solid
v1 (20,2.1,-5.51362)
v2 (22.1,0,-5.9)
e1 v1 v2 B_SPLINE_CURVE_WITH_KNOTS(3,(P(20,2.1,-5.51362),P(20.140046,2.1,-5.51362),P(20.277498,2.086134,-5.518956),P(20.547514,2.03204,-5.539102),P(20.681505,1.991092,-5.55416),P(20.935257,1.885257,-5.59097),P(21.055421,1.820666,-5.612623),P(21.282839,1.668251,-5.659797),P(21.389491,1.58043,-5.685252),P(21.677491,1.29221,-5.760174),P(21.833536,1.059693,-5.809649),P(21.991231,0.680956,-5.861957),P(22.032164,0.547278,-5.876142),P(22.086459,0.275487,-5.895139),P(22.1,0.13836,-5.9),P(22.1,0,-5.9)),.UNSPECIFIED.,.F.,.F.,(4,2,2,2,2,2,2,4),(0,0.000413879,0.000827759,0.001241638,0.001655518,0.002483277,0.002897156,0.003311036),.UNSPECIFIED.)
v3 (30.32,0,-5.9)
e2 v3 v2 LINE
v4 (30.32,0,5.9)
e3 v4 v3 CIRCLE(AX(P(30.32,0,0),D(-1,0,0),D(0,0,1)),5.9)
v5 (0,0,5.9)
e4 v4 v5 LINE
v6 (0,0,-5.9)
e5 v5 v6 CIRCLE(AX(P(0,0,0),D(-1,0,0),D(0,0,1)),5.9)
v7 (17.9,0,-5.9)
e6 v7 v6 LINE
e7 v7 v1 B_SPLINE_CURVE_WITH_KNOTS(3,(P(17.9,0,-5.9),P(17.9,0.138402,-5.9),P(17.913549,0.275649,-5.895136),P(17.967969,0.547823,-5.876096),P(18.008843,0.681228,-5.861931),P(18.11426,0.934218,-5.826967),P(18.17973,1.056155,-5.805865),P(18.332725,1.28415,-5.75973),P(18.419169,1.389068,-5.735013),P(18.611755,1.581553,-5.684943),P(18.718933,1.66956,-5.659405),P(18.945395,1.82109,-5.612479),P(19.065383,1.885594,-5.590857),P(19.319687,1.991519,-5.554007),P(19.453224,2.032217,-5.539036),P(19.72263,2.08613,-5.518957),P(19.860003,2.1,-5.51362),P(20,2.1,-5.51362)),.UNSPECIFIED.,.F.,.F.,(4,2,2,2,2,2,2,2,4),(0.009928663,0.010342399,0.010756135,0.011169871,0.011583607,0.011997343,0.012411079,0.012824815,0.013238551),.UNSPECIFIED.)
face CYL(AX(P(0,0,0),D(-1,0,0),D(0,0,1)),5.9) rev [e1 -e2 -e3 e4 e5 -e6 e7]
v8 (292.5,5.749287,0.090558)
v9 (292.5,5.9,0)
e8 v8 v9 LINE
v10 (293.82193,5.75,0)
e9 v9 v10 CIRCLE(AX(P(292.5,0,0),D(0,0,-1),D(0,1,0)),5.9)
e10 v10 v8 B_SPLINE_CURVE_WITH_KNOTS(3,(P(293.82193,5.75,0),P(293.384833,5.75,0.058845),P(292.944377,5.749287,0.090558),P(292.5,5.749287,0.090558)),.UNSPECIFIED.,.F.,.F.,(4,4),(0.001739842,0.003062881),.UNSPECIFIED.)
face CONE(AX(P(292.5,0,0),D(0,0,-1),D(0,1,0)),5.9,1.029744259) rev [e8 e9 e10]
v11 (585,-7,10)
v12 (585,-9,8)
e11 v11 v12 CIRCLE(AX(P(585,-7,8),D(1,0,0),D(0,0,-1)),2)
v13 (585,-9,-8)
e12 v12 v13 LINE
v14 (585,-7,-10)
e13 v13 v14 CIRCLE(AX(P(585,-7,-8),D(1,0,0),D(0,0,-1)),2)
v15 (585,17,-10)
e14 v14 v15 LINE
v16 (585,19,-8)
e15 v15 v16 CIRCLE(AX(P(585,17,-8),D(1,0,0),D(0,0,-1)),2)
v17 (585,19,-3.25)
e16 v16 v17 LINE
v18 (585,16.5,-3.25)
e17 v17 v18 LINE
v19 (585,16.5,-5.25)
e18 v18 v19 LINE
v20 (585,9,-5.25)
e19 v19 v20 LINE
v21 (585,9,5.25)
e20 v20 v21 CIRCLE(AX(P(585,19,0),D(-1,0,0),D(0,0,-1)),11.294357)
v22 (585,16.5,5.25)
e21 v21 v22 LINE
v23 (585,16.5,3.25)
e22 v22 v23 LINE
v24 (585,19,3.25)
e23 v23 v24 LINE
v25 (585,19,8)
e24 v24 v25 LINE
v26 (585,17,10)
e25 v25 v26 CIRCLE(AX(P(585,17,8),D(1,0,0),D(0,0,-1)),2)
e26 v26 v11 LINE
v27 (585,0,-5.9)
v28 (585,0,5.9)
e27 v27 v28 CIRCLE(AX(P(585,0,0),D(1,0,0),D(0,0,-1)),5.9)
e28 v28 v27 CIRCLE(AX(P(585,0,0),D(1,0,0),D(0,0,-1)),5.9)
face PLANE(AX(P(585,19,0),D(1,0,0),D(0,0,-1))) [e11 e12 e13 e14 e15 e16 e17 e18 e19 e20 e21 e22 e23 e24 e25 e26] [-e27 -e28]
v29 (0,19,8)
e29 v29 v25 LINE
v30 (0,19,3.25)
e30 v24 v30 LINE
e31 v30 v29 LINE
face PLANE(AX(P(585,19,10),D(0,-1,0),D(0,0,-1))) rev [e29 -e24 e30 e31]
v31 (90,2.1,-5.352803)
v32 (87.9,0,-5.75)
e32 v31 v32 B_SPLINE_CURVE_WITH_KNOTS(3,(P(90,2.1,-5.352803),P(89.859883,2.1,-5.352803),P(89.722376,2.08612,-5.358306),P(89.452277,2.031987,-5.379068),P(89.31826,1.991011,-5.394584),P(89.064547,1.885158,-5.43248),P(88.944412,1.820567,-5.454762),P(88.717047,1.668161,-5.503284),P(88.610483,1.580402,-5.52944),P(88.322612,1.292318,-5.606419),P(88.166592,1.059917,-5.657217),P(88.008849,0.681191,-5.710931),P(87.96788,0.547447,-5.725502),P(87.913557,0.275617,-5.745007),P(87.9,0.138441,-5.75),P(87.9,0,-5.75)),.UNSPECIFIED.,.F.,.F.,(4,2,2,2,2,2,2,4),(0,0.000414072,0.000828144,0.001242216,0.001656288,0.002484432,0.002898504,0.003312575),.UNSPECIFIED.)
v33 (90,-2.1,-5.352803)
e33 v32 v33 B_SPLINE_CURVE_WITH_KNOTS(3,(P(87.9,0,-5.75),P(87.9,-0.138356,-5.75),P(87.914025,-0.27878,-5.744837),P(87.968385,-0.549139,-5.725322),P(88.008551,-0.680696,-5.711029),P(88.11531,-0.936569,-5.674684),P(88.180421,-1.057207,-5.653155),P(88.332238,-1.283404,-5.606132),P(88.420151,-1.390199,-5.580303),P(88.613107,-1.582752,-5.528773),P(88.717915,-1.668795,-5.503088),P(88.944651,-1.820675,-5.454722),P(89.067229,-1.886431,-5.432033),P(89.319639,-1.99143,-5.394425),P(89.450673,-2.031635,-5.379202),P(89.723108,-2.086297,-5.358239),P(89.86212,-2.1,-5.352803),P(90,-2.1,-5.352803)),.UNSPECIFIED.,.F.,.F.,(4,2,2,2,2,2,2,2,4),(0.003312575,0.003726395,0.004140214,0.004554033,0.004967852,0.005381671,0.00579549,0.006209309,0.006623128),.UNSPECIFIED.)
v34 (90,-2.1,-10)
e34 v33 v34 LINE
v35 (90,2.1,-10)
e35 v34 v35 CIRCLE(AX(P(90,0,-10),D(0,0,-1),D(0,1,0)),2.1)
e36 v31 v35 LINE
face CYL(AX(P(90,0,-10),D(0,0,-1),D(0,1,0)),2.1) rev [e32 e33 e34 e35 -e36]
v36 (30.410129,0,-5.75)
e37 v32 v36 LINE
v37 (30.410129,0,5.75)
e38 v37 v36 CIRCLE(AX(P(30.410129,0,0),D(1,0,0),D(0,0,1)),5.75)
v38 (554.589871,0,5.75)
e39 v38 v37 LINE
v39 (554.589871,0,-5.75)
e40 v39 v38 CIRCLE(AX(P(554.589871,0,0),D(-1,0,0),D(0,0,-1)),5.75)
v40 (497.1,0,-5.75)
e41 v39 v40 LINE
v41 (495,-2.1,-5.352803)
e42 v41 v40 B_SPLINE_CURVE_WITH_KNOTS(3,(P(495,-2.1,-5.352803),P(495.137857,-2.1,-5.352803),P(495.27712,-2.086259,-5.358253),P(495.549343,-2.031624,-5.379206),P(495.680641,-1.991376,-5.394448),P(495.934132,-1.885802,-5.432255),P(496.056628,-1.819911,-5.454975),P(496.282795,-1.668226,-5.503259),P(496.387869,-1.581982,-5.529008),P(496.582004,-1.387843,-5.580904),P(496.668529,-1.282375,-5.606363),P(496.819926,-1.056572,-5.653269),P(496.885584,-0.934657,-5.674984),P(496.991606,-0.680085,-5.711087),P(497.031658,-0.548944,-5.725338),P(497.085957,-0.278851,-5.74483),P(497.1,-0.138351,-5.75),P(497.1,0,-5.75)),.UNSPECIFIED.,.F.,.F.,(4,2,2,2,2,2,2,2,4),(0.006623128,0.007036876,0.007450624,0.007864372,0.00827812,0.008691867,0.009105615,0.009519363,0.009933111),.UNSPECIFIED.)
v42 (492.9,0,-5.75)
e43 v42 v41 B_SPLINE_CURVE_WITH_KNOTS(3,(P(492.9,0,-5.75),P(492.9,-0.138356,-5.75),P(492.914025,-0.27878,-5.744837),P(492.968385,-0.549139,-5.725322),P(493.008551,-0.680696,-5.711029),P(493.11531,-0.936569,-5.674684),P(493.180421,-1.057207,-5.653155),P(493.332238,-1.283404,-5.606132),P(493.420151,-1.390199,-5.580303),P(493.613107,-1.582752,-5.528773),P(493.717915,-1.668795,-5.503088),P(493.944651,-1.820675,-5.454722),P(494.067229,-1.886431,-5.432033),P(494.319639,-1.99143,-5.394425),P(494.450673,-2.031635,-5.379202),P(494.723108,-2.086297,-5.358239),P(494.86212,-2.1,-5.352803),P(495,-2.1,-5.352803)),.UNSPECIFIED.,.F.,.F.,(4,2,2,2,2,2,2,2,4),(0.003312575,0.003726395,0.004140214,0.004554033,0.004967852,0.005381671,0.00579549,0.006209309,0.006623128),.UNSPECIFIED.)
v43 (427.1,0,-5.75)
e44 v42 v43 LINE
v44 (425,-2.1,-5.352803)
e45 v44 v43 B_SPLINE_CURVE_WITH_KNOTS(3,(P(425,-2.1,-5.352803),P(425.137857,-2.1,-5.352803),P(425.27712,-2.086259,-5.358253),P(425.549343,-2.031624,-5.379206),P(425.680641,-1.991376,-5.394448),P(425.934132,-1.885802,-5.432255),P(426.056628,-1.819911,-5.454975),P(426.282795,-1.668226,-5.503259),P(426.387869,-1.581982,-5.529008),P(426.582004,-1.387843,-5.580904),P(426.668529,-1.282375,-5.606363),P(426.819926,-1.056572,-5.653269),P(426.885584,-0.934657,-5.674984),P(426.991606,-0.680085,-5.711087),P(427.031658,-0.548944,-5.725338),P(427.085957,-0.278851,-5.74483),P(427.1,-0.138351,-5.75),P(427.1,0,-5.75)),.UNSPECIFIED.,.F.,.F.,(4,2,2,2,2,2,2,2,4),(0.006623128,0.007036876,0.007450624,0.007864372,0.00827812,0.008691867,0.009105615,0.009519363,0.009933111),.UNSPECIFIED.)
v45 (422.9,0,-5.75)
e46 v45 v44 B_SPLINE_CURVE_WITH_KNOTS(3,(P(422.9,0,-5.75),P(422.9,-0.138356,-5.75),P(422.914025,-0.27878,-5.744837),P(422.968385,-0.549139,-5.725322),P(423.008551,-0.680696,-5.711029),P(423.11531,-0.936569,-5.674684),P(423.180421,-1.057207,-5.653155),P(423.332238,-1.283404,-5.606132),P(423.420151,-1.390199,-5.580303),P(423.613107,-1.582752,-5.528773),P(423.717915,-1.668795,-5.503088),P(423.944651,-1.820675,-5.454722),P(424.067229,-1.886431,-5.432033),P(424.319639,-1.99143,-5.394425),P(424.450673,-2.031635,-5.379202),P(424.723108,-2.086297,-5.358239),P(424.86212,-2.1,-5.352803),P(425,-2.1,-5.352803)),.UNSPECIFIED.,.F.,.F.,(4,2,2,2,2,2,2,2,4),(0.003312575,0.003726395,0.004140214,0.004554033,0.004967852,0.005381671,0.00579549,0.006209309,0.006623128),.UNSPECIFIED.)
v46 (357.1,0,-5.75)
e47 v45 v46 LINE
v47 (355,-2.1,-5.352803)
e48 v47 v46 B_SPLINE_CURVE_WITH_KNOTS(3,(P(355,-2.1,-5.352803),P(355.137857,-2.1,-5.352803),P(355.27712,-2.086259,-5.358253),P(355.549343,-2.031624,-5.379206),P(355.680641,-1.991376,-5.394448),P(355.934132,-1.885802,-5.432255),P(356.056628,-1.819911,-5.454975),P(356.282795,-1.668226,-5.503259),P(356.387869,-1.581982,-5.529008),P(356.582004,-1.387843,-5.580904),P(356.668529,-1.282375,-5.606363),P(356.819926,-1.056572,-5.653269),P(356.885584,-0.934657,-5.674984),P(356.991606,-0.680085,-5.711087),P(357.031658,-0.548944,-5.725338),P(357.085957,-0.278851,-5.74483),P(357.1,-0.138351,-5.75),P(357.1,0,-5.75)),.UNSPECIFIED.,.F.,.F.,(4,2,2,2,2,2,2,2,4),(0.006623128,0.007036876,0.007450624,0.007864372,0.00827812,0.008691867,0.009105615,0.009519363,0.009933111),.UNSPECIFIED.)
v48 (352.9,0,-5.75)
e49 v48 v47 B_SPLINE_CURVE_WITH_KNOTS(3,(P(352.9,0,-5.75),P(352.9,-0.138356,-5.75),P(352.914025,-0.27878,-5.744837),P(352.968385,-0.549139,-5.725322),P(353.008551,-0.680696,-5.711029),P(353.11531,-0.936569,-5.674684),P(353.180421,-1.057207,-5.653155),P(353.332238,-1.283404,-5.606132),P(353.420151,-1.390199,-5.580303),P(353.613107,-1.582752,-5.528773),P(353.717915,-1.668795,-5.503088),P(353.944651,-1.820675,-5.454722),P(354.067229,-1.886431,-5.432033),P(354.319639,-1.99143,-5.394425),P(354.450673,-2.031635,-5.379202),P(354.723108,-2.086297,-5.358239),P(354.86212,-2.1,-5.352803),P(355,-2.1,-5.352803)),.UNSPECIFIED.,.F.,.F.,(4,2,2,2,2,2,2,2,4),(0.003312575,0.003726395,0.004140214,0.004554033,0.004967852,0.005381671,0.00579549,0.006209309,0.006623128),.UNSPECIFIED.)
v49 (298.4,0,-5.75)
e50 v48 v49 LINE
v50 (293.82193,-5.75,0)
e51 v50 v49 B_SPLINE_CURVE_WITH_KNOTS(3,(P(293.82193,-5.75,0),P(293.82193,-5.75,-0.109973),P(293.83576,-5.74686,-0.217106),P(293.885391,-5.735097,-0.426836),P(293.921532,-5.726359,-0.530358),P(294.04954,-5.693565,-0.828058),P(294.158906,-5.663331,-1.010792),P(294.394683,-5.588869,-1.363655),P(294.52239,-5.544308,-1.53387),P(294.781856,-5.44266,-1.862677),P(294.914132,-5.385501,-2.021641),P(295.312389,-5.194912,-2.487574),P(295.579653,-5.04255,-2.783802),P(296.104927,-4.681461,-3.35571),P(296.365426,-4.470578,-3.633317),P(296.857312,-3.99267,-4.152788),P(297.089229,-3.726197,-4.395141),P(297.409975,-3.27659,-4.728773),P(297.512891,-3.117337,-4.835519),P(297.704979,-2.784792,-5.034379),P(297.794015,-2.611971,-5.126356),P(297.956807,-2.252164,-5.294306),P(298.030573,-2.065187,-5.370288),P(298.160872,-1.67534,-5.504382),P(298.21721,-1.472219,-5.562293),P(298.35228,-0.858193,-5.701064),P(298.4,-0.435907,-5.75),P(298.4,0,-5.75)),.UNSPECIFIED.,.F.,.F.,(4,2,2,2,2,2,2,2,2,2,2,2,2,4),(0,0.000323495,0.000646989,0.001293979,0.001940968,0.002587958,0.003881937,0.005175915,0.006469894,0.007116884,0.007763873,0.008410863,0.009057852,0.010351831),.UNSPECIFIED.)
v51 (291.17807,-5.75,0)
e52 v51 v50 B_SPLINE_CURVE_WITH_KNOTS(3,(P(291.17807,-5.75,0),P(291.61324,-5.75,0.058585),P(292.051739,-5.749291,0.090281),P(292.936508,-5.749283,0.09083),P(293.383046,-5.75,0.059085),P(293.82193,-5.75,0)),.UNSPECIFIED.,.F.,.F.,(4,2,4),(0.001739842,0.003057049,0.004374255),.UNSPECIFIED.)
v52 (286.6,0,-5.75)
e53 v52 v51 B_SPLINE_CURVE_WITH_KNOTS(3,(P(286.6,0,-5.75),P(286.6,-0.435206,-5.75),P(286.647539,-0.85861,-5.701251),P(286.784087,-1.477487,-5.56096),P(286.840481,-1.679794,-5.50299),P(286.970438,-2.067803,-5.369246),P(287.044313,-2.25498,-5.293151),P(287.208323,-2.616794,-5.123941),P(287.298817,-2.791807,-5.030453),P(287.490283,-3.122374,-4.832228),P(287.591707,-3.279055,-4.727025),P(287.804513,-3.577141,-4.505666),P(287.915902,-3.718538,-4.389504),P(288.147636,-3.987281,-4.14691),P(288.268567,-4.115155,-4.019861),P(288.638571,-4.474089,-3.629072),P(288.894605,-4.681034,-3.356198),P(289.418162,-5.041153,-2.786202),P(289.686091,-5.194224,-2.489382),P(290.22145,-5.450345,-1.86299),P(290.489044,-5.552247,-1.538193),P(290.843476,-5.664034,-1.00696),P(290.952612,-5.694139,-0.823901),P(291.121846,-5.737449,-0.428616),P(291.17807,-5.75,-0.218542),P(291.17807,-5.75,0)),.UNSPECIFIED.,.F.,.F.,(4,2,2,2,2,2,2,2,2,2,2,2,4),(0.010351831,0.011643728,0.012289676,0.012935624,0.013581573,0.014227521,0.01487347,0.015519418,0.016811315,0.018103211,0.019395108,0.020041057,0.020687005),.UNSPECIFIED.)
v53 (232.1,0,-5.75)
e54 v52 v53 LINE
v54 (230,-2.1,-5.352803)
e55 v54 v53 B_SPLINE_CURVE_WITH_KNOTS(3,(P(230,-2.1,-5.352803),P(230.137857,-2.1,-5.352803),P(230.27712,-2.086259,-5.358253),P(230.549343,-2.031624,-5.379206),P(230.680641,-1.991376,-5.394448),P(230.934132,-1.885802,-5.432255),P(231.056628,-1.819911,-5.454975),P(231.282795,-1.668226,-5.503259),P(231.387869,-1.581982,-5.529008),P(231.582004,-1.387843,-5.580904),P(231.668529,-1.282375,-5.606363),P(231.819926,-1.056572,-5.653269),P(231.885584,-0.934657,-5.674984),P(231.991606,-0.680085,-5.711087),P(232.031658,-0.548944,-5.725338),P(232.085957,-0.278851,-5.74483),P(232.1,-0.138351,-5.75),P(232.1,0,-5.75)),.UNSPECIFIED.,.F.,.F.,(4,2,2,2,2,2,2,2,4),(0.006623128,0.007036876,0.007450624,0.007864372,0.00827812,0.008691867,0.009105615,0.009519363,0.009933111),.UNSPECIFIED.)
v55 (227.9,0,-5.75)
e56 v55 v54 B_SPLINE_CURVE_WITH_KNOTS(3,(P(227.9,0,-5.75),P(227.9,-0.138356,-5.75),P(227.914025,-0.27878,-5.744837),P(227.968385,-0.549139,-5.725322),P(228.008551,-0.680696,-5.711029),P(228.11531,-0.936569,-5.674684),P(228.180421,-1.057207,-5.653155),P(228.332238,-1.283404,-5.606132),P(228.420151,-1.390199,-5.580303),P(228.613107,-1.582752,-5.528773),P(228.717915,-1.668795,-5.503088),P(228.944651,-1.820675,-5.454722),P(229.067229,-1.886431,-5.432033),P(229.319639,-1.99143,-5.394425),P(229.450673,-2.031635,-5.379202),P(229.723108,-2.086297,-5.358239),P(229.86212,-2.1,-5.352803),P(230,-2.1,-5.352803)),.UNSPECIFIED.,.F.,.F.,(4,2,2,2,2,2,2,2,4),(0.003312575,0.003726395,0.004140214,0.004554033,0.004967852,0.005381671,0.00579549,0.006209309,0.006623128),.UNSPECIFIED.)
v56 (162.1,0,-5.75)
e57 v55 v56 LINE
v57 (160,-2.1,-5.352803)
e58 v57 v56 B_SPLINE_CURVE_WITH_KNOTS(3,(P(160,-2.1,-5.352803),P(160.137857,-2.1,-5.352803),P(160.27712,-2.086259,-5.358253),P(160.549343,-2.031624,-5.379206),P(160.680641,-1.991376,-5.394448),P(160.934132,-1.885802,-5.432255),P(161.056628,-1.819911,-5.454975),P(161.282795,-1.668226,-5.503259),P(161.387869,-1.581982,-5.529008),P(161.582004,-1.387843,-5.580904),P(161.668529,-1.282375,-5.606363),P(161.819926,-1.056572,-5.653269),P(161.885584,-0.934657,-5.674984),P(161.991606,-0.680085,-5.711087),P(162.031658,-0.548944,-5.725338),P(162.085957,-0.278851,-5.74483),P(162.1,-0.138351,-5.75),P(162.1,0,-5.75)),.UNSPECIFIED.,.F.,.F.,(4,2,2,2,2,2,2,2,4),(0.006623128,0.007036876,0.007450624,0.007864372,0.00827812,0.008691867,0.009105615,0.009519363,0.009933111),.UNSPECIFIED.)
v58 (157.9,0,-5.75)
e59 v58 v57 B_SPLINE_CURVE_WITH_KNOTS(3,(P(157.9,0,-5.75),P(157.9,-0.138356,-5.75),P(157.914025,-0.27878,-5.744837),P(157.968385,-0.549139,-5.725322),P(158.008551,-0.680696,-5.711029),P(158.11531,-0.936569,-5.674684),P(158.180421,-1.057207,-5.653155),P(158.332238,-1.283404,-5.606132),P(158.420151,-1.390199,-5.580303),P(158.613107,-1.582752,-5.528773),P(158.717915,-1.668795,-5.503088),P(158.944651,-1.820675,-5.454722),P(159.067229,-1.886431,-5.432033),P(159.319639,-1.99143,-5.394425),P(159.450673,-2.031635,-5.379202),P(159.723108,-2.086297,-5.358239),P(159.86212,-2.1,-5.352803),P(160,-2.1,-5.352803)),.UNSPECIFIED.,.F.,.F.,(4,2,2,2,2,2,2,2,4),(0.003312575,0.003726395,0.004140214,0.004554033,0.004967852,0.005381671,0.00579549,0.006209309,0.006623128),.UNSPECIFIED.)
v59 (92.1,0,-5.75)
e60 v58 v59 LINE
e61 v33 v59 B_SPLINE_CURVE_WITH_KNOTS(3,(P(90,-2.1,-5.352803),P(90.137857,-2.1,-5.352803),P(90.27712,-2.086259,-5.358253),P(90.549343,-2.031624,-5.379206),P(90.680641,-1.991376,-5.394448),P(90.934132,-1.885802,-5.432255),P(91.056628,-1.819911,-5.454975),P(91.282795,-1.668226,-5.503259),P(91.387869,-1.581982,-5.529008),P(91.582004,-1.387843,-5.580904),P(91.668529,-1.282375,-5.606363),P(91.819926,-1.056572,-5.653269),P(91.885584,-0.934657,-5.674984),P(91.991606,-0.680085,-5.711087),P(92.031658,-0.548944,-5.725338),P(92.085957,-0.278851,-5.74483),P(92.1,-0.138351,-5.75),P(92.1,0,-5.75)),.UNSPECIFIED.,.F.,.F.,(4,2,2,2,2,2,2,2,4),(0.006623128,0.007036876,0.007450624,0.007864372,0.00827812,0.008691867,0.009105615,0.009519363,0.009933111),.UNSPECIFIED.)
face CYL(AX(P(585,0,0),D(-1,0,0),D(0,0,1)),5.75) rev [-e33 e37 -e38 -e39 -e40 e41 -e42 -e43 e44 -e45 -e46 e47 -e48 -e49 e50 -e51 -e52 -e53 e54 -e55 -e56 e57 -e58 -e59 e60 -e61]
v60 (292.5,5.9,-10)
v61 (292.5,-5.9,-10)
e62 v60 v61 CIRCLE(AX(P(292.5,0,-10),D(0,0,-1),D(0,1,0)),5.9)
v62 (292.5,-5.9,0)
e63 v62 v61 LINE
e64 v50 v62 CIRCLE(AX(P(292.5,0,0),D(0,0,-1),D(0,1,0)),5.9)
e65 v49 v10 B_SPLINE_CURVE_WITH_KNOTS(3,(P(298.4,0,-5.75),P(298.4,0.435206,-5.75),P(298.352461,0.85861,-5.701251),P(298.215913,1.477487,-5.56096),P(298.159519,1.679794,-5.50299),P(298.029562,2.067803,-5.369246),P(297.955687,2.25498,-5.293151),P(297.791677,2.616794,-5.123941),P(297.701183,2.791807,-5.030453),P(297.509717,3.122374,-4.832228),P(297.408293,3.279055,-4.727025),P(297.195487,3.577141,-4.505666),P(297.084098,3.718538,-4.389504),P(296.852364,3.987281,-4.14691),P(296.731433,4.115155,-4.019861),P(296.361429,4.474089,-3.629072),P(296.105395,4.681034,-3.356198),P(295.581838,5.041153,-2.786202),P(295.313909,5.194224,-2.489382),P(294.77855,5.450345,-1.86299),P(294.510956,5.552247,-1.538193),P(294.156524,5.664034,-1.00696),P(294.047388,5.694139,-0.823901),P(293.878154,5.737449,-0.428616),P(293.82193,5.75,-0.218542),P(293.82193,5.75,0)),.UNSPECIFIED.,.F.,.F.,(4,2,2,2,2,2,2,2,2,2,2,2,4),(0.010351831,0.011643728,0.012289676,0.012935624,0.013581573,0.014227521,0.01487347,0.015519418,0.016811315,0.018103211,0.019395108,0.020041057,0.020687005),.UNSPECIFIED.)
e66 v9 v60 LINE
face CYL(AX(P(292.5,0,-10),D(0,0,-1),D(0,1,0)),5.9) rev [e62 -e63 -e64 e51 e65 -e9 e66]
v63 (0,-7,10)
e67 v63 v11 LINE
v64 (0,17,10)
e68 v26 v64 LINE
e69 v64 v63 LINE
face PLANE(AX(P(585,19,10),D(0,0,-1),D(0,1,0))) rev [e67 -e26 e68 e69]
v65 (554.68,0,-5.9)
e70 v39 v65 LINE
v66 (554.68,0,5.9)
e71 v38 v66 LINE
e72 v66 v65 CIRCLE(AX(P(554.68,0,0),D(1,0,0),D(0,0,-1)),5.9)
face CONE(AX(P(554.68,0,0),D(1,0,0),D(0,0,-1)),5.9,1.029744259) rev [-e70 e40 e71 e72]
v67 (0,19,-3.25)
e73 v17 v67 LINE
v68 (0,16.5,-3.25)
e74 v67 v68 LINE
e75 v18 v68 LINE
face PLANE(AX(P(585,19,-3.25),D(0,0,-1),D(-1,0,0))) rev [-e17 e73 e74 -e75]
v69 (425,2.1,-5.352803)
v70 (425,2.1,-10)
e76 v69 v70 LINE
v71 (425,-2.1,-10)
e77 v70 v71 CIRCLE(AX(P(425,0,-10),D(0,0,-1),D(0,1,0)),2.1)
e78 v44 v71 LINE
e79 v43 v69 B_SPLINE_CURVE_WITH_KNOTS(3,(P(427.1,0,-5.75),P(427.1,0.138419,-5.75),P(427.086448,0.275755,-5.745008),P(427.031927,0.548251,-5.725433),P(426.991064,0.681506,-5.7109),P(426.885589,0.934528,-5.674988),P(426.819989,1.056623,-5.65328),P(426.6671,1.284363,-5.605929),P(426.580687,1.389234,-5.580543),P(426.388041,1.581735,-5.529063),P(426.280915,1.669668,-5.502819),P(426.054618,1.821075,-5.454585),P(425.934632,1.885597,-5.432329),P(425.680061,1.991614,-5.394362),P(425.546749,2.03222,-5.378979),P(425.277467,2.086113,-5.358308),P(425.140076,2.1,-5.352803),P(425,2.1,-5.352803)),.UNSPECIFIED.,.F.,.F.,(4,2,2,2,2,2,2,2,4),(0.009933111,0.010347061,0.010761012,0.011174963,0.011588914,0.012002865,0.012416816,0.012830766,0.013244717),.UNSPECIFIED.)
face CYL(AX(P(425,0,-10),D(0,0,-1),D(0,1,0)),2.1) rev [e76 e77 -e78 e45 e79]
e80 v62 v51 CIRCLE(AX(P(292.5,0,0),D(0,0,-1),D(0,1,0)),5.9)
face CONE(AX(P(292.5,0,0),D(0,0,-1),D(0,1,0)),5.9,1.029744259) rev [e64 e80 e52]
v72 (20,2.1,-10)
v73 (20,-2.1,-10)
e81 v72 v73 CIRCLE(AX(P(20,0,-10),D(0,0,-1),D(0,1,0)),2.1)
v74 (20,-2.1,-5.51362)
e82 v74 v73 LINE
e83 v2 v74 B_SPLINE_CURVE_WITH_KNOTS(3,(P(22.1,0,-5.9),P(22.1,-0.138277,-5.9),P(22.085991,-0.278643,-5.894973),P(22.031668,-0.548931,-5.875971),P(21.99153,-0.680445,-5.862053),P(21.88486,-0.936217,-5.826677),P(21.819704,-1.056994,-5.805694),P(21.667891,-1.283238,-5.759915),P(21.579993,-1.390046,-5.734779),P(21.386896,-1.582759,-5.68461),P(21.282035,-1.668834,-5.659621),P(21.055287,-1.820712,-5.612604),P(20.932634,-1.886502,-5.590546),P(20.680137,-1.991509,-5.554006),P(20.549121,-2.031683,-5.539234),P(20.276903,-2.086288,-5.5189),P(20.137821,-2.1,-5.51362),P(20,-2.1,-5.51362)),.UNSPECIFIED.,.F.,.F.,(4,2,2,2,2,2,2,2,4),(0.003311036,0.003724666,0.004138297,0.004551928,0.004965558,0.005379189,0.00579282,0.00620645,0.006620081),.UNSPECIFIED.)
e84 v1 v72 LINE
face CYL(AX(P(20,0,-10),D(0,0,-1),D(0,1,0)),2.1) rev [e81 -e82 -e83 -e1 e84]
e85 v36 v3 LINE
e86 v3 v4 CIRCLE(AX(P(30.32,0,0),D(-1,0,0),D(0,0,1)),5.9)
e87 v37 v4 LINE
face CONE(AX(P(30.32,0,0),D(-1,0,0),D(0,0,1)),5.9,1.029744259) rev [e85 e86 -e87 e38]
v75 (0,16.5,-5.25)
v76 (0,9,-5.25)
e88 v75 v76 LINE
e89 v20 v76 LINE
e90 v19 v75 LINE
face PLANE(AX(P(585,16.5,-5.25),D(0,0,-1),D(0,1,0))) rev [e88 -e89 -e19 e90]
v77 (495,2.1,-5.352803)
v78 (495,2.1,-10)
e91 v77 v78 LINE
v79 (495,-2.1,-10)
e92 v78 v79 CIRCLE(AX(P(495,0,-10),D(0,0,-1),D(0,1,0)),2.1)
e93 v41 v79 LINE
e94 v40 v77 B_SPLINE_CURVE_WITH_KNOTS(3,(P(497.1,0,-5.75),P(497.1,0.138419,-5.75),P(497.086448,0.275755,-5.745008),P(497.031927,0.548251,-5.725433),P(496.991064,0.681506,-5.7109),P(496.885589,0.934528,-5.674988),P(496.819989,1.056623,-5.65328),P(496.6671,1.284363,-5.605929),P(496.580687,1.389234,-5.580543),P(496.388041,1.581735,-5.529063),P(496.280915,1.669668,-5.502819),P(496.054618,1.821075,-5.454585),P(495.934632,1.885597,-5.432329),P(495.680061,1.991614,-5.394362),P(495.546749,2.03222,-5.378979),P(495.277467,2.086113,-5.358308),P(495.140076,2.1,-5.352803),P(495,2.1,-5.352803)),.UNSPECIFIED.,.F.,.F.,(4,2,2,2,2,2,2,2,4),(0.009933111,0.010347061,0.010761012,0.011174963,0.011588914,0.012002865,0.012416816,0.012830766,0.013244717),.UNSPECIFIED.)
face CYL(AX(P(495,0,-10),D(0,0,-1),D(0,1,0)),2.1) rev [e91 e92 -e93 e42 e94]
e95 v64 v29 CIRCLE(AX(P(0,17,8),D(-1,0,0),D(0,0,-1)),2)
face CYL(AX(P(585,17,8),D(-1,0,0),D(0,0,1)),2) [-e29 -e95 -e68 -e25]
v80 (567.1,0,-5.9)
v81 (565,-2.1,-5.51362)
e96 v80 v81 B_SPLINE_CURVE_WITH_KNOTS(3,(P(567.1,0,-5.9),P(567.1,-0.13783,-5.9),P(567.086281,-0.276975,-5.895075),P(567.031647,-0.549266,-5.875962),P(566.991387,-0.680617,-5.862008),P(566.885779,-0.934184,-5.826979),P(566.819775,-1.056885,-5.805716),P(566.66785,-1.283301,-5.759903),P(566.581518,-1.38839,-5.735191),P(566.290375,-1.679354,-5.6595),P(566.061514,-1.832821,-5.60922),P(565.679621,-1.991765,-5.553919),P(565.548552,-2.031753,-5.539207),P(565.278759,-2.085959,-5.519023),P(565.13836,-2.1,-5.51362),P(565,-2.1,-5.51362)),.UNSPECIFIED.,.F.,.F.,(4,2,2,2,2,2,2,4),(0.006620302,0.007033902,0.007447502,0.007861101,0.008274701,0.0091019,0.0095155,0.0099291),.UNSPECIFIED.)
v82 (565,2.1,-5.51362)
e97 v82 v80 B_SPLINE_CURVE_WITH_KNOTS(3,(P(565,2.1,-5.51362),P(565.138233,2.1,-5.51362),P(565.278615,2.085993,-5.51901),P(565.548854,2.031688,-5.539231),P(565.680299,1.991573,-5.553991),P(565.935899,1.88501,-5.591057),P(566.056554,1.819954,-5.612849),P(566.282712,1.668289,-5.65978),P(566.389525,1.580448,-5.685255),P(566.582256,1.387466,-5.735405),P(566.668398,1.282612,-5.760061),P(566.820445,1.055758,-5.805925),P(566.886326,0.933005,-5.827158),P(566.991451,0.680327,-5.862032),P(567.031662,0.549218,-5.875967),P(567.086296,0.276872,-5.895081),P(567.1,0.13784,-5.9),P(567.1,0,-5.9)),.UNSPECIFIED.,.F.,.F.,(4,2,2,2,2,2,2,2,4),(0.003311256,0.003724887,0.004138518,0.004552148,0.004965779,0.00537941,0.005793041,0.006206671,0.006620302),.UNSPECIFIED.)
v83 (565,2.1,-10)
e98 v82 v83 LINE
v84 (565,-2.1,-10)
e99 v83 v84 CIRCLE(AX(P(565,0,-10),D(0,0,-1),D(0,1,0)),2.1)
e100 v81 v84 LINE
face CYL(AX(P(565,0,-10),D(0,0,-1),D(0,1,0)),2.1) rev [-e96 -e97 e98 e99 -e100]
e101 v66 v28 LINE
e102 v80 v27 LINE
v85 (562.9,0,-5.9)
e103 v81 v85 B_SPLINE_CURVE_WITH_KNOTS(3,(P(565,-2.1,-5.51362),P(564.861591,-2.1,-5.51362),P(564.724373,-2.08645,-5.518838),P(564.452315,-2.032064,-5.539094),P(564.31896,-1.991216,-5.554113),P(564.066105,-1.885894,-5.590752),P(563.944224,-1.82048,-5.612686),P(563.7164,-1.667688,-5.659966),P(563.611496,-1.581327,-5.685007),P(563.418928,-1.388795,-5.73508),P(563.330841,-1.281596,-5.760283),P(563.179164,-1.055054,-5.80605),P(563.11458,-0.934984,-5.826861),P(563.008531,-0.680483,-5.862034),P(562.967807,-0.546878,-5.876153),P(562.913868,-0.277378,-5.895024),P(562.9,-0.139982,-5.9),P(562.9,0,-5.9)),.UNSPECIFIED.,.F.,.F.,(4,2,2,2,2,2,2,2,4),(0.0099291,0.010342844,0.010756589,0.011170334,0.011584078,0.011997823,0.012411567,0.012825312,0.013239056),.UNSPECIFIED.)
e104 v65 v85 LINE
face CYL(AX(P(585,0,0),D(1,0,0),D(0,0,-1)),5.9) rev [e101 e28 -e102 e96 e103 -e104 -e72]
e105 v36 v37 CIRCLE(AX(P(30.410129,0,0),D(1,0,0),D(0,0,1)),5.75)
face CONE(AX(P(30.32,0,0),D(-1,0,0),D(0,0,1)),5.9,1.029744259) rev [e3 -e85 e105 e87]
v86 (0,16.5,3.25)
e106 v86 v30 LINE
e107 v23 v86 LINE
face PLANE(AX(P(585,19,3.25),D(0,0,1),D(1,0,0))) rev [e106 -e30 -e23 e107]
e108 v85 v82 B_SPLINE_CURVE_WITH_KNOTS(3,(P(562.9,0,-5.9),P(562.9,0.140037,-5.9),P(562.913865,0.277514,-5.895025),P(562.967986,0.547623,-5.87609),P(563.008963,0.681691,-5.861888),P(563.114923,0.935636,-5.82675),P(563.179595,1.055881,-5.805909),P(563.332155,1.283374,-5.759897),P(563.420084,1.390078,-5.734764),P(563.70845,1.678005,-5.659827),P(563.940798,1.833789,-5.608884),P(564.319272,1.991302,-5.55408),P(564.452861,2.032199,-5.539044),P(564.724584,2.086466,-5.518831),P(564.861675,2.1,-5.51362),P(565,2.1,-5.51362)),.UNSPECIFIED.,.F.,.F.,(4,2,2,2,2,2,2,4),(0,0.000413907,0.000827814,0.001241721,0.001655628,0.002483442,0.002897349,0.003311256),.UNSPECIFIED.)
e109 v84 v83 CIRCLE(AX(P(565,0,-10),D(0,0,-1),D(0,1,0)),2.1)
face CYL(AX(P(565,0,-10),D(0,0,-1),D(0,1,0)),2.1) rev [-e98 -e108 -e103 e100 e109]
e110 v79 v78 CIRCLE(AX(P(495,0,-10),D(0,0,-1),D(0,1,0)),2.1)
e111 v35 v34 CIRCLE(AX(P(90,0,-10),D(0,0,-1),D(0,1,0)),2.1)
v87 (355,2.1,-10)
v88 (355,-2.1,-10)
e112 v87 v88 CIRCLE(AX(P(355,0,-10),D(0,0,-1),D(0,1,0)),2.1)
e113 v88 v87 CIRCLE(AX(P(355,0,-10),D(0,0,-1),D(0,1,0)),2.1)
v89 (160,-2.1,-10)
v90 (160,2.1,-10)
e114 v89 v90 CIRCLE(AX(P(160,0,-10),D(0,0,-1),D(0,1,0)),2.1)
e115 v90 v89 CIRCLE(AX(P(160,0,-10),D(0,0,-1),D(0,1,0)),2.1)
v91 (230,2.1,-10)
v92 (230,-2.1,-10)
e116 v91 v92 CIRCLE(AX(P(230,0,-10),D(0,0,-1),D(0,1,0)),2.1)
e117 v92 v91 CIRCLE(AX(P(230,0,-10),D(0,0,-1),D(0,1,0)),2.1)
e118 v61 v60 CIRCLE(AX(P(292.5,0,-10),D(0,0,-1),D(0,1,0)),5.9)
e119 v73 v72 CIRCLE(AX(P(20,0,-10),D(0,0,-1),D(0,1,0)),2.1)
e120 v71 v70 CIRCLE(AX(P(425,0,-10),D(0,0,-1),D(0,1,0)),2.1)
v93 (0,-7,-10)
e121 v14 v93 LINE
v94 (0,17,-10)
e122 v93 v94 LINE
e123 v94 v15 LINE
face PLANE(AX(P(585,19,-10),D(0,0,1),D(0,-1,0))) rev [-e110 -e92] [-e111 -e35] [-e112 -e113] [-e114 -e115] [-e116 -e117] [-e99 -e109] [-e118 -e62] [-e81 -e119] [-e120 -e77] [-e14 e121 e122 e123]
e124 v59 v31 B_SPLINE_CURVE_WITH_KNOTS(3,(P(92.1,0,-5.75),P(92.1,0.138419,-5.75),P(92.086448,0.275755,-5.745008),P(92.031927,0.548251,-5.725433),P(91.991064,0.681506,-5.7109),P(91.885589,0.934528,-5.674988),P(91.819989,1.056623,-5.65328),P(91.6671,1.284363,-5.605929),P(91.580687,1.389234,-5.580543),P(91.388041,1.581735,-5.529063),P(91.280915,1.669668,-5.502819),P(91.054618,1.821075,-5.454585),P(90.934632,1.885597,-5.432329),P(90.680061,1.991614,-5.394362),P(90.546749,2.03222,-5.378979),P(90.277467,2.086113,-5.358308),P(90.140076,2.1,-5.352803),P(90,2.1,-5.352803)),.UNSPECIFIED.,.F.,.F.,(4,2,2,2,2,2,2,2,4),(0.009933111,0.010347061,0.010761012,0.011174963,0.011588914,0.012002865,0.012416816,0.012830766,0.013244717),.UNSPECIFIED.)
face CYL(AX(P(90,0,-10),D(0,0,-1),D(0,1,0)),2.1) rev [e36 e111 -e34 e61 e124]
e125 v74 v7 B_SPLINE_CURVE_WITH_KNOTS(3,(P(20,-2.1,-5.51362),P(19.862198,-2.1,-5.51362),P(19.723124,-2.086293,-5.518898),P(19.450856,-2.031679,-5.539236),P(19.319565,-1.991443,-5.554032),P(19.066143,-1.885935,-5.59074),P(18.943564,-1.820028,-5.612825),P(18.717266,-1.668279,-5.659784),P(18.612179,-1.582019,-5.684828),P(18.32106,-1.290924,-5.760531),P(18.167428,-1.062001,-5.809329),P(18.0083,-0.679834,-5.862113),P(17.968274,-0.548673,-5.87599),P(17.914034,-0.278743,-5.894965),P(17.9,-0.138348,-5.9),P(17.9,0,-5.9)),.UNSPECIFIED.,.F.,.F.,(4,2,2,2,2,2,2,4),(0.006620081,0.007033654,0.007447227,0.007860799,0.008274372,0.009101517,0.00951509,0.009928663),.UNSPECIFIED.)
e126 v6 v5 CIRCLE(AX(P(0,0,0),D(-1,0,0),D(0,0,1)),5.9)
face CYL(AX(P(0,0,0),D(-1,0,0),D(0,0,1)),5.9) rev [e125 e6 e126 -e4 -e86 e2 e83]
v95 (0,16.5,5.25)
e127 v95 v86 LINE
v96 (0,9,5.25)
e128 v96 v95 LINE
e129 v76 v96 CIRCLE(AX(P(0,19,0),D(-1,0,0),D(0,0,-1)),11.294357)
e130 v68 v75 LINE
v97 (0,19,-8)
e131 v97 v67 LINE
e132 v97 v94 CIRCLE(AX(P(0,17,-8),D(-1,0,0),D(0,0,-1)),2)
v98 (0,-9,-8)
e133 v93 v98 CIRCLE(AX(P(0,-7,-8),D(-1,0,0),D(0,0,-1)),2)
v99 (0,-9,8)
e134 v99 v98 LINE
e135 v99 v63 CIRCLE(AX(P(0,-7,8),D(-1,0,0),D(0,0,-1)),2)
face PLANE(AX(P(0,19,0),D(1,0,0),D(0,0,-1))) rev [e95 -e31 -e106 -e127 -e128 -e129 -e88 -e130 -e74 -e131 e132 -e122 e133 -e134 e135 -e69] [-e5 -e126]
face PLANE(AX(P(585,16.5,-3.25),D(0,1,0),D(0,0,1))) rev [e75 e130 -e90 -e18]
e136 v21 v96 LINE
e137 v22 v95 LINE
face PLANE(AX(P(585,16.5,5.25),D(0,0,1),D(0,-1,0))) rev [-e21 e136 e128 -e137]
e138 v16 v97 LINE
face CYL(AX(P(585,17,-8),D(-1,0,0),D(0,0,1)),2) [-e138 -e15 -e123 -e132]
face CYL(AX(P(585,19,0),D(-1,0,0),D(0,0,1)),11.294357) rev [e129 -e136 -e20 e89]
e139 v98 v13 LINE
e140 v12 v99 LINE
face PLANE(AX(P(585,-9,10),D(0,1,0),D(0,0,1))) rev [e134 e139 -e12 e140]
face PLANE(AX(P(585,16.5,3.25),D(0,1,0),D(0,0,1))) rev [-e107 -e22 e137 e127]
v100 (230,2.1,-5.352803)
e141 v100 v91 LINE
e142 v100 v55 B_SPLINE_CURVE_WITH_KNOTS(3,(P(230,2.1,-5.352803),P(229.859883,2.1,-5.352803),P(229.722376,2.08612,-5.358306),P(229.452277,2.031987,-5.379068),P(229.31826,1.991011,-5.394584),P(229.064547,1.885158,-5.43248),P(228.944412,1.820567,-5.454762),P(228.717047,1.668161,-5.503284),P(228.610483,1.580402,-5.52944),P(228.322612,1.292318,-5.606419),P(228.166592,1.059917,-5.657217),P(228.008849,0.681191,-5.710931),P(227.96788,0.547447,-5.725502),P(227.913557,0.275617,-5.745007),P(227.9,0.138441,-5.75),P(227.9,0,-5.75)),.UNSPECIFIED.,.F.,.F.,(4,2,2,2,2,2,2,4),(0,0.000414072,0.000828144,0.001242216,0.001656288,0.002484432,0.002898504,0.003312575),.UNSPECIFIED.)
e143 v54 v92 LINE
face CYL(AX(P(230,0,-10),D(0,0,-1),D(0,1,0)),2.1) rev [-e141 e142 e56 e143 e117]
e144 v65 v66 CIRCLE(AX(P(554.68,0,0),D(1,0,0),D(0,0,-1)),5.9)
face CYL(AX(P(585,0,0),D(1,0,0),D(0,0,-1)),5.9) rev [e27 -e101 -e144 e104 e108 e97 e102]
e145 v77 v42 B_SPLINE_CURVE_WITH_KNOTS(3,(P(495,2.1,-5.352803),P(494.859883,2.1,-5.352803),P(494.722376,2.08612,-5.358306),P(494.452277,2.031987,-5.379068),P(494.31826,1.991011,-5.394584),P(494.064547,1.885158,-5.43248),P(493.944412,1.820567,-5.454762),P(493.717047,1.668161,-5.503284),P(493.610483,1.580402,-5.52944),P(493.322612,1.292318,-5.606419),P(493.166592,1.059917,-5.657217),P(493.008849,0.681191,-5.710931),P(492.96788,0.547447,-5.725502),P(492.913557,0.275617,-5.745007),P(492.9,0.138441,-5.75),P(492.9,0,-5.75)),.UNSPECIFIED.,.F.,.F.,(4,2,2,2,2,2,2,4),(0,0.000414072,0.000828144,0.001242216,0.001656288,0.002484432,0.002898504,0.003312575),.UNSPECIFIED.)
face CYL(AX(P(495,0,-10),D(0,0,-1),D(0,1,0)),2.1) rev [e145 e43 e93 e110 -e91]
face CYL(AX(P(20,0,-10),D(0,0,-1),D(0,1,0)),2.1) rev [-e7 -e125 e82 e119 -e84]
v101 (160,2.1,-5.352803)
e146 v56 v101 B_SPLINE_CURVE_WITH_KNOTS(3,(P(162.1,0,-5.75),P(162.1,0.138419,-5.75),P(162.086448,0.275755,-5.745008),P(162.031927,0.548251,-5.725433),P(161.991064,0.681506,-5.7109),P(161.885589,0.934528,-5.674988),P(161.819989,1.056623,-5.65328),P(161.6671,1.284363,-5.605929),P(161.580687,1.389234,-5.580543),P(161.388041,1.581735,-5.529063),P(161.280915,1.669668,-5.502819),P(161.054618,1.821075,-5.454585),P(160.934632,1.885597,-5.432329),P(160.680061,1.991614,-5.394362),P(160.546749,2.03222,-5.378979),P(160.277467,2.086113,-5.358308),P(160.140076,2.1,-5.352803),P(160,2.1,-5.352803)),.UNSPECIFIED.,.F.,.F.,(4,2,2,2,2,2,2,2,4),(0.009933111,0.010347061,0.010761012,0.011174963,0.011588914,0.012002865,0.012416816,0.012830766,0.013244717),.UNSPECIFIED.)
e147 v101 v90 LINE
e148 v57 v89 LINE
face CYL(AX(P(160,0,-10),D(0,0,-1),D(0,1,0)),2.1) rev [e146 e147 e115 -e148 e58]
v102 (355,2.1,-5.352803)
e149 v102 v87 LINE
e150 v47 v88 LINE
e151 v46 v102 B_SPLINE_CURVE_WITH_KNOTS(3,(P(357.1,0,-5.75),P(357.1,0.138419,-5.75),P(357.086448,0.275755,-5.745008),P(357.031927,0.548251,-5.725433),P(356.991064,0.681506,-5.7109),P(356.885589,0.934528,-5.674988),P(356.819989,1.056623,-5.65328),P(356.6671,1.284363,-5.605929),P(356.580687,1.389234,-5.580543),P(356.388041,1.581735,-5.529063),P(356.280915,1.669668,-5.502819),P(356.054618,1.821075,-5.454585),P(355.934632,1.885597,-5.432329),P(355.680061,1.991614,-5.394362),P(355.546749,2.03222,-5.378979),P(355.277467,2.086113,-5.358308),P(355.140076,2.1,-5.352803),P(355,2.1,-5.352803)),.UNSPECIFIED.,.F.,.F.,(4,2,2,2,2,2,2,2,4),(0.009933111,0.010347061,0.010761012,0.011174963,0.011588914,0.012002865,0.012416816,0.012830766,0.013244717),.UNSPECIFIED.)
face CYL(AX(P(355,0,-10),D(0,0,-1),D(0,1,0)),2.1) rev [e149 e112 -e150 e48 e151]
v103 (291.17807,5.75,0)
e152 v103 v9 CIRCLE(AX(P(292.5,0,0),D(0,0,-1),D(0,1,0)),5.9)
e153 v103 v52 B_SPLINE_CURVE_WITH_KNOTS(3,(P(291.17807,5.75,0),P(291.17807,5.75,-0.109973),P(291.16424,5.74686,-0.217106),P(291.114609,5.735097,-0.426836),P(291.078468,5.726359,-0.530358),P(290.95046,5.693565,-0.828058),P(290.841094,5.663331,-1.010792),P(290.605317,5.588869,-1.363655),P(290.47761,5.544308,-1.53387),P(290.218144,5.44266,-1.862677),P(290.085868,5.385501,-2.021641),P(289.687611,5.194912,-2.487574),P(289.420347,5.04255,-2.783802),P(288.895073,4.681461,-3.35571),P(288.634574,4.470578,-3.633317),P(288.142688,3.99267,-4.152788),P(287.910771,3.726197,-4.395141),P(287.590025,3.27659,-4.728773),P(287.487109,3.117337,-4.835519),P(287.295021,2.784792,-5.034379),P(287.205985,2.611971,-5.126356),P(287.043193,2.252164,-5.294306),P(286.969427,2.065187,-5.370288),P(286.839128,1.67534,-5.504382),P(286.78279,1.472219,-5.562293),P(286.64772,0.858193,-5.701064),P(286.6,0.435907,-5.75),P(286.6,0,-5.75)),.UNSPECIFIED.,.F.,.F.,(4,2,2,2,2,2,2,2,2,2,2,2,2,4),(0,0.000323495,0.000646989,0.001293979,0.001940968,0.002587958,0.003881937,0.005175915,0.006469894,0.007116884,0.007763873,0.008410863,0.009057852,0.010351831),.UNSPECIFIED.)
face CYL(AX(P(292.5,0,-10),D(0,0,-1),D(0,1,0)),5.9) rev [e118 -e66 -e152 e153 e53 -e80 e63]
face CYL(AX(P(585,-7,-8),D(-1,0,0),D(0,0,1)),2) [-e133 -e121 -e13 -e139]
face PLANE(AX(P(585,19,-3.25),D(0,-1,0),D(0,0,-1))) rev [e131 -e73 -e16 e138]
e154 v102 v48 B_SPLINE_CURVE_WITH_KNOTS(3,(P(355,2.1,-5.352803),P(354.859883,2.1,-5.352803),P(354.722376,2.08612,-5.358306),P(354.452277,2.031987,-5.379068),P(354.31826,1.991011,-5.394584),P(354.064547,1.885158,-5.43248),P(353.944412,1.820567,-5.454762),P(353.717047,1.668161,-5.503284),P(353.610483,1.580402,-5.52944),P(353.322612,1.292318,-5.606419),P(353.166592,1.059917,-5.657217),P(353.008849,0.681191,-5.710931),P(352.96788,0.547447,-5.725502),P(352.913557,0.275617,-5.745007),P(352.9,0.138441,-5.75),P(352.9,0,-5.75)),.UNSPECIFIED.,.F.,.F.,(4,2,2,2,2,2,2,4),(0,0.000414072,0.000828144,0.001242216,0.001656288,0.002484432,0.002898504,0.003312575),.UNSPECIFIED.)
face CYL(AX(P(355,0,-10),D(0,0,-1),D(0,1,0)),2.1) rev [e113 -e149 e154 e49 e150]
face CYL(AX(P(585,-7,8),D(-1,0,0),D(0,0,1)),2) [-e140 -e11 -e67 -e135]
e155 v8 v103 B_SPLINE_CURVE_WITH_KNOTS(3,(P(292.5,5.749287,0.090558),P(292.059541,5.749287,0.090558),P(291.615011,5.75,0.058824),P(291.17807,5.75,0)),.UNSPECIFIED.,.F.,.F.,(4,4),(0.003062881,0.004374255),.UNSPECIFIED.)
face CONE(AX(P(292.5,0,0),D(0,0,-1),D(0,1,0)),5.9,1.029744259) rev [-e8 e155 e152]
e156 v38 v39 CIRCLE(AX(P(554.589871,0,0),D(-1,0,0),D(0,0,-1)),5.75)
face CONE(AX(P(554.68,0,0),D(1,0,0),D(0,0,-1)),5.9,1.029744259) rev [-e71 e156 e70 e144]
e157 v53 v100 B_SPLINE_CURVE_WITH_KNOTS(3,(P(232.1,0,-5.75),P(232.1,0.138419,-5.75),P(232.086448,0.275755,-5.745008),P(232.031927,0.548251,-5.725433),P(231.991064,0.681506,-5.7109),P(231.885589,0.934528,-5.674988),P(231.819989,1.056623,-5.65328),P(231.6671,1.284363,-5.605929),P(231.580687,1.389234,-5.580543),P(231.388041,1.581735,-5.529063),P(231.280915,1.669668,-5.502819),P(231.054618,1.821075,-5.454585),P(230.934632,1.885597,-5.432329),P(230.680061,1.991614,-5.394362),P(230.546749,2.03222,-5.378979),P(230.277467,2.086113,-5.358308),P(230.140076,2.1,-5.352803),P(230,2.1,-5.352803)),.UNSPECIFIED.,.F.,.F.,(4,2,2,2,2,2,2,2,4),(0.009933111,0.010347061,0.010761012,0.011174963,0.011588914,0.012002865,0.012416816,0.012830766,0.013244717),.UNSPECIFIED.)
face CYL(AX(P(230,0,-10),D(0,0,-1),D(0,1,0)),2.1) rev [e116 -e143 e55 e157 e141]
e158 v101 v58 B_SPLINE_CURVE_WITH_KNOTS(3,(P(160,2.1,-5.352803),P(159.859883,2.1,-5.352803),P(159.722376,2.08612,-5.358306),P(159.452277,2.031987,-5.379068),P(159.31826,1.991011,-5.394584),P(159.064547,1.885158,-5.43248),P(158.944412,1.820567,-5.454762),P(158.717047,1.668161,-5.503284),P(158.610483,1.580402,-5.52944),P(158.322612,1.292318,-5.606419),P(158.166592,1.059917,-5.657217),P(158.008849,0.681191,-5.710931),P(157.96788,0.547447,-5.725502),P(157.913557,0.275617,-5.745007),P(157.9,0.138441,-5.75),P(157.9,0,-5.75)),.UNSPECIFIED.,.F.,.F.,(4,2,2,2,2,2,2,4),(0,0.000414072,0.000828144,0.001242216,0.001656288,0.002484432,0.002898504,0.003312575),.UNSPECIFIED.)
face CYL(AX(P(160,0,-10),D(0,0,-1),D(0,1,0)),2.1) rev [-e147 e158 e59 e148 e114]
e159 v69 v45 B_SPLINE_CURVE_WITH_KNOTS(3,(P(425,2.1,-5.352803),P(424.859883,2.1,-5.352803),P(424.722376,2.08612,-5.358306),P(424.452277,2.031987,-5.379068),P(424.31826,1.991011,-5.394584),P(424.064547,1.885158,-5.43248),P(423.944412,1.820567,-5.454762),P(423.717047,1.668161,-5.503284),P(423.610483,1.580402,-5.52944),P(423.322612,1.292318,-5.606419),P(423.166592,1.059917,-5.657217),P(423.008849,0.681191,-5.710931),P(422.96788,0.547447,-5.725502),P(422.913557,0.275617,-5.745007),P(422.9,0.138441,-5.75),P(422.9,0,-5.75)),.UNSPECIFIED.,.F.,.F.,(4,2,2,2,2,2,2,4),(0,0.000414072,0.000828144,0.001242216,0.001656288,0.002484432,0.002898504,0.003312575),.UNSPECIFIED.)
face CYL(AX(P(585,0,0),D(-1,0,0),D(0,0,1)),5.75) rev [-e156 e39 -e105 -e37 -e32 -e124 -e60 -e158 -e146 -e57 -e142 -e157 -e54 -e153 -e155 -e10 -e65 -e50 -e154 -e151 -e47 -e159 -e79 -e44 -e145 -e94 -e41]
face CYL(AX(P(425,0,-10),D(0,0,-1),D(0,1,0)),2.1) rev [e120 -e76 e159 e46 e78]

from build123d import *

# Parameters (mm, degrees)
SKETCH1_R               = 5.75
EXTRUDE1_DEPTH          = 585
FILLET1_R               = 2
G1_4_TAPPED_HOLE1_D     = 11.8
G1_4_TAPPED_HOLE1_DEPTH = 30.32
G1_4_TAPPED_HOLE1_TIP   = 3.545077652
G1_4_TAPPED_HOLE2_D     = 11.8
G1_4_TAPPED_HOLE2_DEPTH = 30.32
G1_4_TAPPED_HOLE2_TIP   = 3.545077652
M5_TAPPED_HOLE2_D       = 4.2
M5_TAPPED_HOLE2_DEPTH   = 8
M5_TAPPED_HOLE2_TIP     = 1.2618073
G1_4_TAPPED_HOLE7_D     = 11.8
G1_4_TAPPED_HOLE7_DEPTH = 10
G1_4_TAPPED_HOLE7_TIP   = 3.545077652


with BuildPart() as part:
    # Sketch1 → Extrude1 (new body)
    with BuildSketch(Plane(origin=(0, 0, 0), x_dir=(0, 0, -1), z_dir=(1, 0, 0))):
        with BuildLine():
            Line((-3.25, 19), (-3.25, 16.5))
            Line((-3.25, 16.5), (-5.25, 16.5))
            Line((-5.25, 16.5), (-5.25, 9))
            ThreePointArc((-5.25, 9), (0, 7.705643002), (5.25, 9))
            Line((5.25, 9), (5.25, 16.5))
            Line((5.25, 16.5), (3.25, 16.5))
            Line((3.25, 16.5), (3.25, 19))
            Line((3.25, 19), (10, 19))
            Line((10, 19), (10, -9))
            Line((10, -9), (-10, -9))
            Line((-10, -9), (-10, 19))
            Line((-10, 19), (-3.25, 19))
        make_face()
        Circle(SKETCH1_R, mode=Mode.SUBTRACT)
    extrude(amount=EXTRUDE1_DEPTH)

    # Fillet1
    fillet1_edges = [part.edges().sort_by_distance(p)[0] for p in [
        (292.5, 19, 10),
        (292.5, 19, -10),
        (292.5, -9, -10),
        (292.5, -9, 10),
    ]]
    fillet(fillet1_edges, radius=FILLET1_R)

    # G1/4 Tapped Hole1
    with Locations(Plane.ZY):
        with Locations((0, 0)):
            Hole(G1_4_TAPPED_HOLE1_D / 2, depth=G1_4_TAPPED_HOLE1_DEPTH)
            with Locations((0, 0, -(G1_4_TAPPED_HOLE1_DEPTH + G1_4_TAPPED_HOLE1_TIP / 2))):  # 118° drill point
                Cone(0, G1_4_TAPPED_HOLE1_D / 2, G1_4_TAPPED_HOLE1_TIP, mode=Mode.SUBTRACT)

    # G1/4 Tapped Hole2
    with Locations(Plane(origin=(585, 0, 0), x_dir=(0, 0, -1), z_dir=(1, 0, 0))):
        with Locations((0, 0)):
            Hole(G1_4_TAPPED_HOLE2_D / 2, depth=G1_4_TAPPED_HOLE2_DEPTH)
            with Locations((0, 0, -(G1_4_TAPPED_HOLE2_DEPTH + G1_4_TAPPED_HOLE2_TIP / 2))):  # 118° drill point
                Cone(0, G1_4_TAPPED_HOLE2_D / 2, G1_4_TAPPED_HOLE2_TIP, mode=Mode.SUBTRACT)

    # M5 Tapped Hole2
    with Locations(Plane(origin=(0, 0, -10), x_dir=(-1, 0, 0), z_dir=(0, 0, -1))):
        with Locations((-565, 0), (-495, 0), (-425, 0), (-355, 0), (-230, 0), (-160, 0), (-90, 0), (-20, 0)):
            Hole(M5_TAPPED_HOLE2_D / 2, depth=M5_TAPPED_HOLE2_DEPTH)
            with Locations((0, 0, -(M5_TAPPED_HOLE2_DEPTH + M5_TAPPED_HOLE2_TIP / 2))):  # 118° drill point
                Cone(0, M5_TAPPED_HOLE2_D / 2, M5_TAPPED_HOLE2_TIP, mode=Mode.SUBTRACT)

    # G1/4 Tapped Hole7
    with Locations(Plane(origin=(0, 0, -10), x_dir=(-1, 0, 0), z_dir=(0, 0, -1))):
        with Locations((-292.5, 0)):
            Hole(G1_4_TAPPED_HOLE7_D / 2, depth=G1_4_TAPPED_HOLE7_DEPTH)
            with Locations((0, 0, -(G1_4_TAPPED_HOLE7_DEPTH + G1_4_TAPPED_HOLE7_TIP / 2))):  # 118° drill point
                Cone(0, G1_4_TAPPED_HOLE7_D / 2, G1_4_TAPPED_HOLE7_TIP, mode=Mode.SUBTRACT)


solid = part.part
